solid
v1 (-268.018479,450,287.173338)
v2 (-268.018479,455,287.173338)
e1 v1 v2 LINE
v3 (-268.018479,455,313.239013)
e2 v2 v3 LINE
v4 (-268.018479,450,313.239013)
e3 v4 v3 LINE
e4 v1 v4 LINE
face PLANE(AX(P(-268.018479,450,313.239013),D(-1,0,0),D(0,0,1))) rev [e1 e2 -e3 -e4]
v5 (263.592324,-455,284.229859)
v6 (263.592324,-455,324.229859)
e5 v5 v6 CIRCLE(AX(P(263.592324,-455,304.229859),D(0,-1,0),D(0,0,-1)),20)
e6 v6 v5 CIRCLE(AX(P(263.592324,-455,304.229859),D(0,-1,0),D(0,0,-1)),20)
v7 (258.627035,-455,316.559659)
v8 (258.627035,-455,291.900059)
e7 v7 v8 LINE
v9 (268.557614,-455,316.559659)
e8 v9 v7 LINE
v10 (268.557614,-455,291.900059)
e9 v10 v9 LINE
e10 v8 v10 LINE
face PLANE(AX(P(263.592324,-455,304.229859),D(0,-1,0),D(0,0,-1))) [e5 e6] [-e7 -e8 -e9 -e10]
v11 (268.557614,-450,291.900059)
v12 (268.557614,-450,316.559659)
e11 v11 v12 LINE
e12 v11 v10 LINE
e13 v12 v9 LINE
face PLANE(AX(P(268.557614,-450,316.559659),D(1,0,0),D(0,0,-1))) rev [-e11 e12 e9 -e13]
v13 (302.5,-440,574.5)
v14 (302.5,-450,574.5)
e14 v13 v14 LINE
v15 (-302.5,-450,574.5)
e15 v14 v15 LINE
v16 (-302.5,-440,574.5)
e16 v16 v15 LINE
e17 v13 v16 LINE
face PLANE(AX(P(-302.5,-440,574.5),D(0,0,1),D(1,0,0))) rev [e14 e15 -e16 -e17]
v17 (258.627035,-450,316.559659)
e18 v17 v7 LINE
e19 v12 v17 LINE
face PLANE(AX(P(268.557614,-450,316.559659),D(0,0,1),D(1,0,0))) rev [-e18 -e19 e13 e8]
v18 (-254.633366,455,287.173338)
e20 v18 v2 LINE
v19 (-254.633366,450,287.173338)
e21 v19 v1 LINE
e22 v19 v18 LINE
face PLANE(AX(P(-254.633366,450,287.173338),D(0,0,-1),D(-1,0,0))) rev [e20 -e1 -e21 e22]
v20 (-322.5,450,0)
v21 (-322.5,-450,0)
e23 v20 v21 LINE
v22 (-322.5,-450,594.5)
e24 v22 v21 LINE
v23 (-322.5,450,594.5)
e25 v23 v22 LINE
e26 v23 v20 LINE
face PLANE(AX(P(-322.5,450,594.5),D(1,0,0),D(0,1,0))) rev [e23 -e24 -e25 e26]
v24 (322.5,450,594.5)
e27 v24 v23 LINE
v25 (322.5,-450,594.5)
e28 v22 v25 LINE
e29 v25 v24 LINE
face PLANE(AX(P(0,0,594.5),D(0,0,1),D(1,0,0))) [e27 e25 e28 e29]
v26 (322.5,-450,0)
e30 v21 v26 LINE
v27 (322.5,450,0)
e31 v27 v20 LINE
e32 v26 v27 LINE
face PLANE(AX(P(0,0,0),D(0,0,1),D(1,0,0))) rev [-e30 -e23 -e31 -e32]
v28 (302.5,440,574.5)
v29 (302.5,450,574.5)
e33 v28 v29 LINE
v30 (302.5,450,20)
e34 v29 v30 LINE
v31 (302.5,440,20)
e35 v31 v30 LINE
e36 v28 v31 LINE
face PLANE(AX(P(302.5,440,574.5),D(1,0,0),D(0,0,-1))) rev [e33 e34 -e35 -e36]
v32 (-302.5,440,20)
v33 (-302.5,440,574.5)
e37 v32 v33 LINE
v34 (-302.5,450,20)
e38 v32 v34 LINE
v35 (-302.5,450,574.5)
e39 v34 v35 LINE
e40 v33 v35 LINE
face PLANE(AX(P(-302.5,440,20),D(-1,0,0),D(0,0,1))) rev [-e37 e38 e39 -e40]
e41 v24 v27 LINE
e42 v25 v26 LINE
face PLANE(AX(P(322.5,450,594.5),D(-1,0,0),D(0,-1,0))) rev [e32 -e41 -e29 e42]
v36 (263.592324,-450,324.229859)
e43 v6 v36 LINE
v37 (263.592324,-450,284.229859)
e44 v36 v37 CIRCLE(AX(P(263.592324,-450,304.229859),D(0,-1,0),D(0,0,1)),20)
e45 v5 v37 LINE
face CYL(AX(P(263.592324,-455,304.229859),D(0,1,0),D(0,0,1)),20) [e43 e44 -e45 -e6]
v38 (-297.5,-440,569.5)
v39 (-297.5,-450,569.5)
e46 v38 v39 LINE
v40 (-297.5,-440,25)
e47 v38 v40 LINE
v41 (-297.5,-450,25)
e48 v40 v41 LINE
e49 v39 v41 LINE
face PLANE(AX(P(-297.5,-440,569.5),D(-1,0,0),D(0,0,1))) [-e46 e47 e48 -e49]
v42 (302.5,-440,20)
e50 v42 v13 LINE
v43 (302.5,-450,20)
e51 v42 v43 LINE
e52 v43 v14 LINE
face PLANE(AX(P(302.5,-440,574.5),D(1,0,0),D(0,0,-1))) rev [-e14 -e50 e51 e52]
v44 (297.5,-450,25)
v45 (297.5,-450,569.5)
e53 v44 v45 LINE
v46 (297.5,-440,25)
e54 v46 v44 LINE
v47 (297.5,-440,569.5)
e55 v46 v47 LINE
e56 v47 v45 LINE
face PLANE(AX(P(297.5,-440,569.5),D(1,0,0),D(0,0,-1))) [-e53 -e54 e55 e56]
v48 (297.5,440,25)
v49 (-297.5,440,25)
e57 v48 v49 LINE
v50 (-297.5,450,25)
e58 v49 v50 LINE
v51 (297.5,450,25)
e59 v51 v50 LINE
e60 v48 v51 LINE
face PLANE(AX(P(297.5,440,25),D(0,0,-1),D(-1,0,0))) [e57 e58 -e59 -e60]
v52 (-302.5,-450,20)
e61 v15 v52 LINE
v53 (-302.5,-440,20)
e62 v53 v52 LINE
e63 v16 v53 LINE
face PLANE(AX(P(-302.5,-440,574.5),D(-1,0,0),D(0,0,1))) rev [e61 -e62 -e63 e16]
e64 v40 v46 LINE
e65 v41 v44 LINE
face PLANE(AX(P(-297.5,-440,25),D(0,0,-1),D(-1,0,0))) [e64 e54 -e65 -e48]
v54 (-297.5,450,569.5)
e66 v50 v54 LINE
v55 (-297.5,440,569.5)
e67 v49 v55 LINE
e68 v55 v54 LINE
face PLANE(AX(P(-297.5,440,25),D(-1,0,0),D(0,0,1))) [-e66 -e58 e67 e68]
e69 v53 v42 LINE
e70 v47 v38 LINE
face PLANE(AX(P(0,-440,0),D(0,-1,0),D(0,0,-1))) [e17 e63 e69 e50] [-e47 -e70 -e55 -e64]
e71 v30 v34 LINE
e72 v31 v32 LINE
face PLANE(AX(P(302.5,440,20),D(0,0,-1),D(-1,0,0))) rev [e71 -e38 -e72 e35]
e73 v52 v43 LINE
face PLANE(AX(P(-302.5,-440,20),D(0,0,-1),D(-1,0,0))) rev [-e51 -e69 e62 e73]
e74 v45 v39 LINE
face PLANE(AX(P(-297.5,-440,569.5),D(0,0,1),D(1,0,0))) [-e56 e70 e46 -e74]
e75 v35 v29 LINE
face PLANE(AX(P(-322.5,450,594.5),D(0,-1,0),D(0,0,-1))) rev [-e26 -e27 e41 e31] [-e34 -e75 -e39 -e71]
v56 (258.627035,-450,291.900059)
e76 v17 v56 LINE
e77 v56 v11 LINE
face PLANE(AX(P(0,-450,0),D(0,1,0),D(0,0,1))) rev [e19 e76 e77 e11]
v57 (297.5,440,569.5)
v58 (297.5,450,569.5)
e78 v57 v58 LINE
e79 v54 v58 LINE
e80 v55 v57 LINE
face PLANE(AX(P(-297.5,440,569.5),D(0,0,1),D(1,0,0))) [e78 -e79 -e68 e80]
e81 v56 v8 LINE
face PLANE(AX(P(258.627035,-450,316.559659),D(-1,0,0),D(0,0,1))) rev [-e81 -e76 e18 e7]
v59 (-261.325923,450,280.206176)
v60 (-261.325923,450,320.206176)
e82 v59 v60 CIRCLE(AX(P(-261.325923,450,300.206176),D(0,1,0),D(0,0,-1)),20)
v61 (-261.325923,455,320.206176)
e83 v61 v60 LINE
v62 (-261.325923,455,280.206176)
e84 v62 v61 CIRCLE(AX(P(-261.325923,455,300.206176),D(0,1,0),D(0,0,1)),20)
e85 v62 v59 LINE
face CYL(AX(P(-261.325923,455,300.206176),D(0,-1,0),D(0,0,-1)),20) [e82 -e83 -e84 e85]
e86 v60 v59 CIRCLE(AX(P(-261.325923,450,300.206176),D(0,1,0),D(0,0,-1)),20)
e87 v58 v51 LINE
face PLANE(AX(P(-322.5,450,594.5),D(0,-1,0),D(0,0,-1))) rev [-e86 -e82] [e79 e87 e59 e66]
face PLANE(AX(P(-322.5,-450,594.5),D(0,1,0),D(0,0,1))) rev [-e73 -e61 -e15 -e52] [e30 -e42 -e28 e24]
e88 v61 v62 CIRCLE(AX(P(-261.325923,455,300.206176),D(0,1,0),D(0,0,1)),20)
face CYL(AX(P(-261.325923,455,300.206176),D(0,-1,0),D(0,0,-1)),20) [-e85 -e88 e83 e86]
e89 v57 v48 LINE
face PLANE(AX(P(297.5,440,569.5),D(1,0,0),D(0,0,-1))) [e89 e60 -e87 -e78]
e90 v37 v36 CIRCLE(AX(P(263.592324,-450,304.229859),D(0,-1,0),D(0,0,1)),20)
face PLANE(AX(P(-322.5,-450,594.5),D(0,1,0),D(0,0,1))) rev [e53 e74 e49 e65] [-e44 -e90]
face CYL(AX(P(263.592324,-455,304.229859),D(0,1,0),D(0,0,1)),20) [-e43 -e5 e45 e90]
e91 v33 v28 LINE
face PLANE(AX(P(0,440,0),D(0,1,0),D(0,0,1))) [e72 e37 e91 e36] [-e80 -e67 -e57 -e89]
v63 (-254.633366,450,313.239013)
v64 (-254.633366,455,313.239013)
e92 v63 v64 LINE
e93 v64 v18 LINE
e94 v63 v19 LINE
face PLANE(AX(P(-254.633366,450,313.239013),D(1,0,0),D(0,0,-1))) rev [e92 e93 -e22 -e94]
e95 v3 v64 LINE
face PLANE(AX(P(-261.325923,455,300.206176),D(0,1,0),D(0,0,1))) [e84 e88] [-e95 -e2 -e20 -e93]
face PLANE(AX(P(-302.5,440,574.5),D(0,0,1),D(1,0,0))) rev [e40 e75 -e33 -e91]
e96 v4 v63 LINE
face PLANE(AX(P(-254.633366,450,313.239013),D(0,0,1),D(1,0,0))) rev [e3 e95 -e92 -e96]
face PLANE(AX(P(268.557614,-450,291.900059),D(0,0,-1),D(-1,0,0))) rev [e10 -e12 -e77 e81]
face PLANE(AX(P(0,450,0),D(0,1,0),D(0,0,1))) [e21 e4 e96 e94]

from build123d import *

# Parameters (mm, degrees)
SKETCH_1_W          = 645
SKETCH_1_H          = 900
EXTRUDE_1_DEPTH     = 594.5
SKETCH_2_W          = 605
SKETCH_2_H          = 554.5
SKETCH_2_W_2        = 595
SKETCH_2_H_2        = 544.5
CUT_EXTRUDE_1_DEPTH = 10
SKETCH_3_R          = 20
EXTRUDE_2_DEPTH     = 5
SKETCH_4_W          = 9.930578971
SKETCH_4_H          = 24.659600502
CUT_EXTRUDE_2_DEPTH = 5
SKETCH_5_W          = 605
SKETCH_5_H          = 554.5
SKETCH_5_W_2        = 595
SKETCH_5_H_2        = 544.5
CUT_EXTRUDE_3_DEPTH = 10
SKETCH_6_R          = 20
EXTRUDE_3_DEPTH     = 5
SKETCH_7_W          = 13.385113247
SKETCH_7_H          = 26.065674485
CUT_EXTRUDE_4_DEPTH = 5


with BuildPart() as part:
    # 草图1 → 凸台-拉伸1 (new body)
    with BuildSketch(Plane.XY):
        Rectangle(SKETCH_1_W, SKETCH_1_H)
    extrude(amount=EXTRUDE_1_DEPTH)

    # 草图2 → 切除-拉伸1 (cut)
    with BuildSketch(Plane.XZ.offset(450)):
        with Locations((0, 297.25)):
            Rectangle(SKETCH_2_W, SKETCH_2_H)
        with Locations((0, 297.25)):
            Rectangle(SKETCH_2_W_2, SKETCH_2_H_2, mode=Mode.SUBTRACT)
    extrude(amount=-CUT_EXTRUDE_1_DEPTH, mode=Mode.SUBTRACT)

    # 草图3 → 凸台-拉伸2 (add)
    with BuildSketch(Plane.XZ.offset(450)):
        with Locations(Location((263.592324158, 304.229859051, 0), (0, 0, 90))):
            Circle(SKETCH_3_R)
    extrude(amount=EXTRUDE_2_DEPTH)

    # 草图4 → 切除-拉伸2 (cut)
    with BuildSketch(Plane.XZ.offset(455)):
        with Locations((263.592324158, 304.229859051)):
            Rectangle(SKETCH_4_W, SKETCH_4_H)
    extrude(amount=-CUT_EXTRUDE_2_DEPTH, mode=Mode.SUBTRACT)

    # 草图5 → 切除-拉伸3 (cut)
    with BuildSketch(Plane(origin=(0, 450, 0), x_dir=(1, 0, 0), z_dir=(0, 1, 0))):
        with Locations((0, -297.25)):
            Rectangle(SKETCH_5_W, SKETCH_5_H)
        with Locations((0, -297.25)):
            Rectangle(SKETCH_5_W_2, SKETCH_5_H_2, mode=Mode.SUBTRACT)
    extrude(amount=-CUT_EXTRUDE_3_DEPTH, mode=Mode.SUBTRACT)

    # 草图6 → 凸台-拉伸3 (add)
    with BuildSketch(Plane(origin=(0, 450, 0), x_dir=(1, 0, 0), z_dir=(0, 1, 0))):
        with Locations(Location((-261.325922866, -300.206175598, 0), (0, 0, 90))):
            Circle(SKETCH_6_R)
    extrude(amount=EXTRUDE_3_DEPTH)

    # 草图7 → 切除-拉伸4 (cut)
    with BuildSketch(Plane(origin=(0, 455, 0), x_dir=(1, 0, 0), z_dir=(0, 1, 0))):
        with Locations((-261.325922867, -300.206175599)):
            Rectangle(SKETCH_7_W, SKETCH_7_H)
    extrude(amount=-CUT_EXTRUDE_4_DEPTH, mode=Mode.SUBTRACT)


solid = part.part
